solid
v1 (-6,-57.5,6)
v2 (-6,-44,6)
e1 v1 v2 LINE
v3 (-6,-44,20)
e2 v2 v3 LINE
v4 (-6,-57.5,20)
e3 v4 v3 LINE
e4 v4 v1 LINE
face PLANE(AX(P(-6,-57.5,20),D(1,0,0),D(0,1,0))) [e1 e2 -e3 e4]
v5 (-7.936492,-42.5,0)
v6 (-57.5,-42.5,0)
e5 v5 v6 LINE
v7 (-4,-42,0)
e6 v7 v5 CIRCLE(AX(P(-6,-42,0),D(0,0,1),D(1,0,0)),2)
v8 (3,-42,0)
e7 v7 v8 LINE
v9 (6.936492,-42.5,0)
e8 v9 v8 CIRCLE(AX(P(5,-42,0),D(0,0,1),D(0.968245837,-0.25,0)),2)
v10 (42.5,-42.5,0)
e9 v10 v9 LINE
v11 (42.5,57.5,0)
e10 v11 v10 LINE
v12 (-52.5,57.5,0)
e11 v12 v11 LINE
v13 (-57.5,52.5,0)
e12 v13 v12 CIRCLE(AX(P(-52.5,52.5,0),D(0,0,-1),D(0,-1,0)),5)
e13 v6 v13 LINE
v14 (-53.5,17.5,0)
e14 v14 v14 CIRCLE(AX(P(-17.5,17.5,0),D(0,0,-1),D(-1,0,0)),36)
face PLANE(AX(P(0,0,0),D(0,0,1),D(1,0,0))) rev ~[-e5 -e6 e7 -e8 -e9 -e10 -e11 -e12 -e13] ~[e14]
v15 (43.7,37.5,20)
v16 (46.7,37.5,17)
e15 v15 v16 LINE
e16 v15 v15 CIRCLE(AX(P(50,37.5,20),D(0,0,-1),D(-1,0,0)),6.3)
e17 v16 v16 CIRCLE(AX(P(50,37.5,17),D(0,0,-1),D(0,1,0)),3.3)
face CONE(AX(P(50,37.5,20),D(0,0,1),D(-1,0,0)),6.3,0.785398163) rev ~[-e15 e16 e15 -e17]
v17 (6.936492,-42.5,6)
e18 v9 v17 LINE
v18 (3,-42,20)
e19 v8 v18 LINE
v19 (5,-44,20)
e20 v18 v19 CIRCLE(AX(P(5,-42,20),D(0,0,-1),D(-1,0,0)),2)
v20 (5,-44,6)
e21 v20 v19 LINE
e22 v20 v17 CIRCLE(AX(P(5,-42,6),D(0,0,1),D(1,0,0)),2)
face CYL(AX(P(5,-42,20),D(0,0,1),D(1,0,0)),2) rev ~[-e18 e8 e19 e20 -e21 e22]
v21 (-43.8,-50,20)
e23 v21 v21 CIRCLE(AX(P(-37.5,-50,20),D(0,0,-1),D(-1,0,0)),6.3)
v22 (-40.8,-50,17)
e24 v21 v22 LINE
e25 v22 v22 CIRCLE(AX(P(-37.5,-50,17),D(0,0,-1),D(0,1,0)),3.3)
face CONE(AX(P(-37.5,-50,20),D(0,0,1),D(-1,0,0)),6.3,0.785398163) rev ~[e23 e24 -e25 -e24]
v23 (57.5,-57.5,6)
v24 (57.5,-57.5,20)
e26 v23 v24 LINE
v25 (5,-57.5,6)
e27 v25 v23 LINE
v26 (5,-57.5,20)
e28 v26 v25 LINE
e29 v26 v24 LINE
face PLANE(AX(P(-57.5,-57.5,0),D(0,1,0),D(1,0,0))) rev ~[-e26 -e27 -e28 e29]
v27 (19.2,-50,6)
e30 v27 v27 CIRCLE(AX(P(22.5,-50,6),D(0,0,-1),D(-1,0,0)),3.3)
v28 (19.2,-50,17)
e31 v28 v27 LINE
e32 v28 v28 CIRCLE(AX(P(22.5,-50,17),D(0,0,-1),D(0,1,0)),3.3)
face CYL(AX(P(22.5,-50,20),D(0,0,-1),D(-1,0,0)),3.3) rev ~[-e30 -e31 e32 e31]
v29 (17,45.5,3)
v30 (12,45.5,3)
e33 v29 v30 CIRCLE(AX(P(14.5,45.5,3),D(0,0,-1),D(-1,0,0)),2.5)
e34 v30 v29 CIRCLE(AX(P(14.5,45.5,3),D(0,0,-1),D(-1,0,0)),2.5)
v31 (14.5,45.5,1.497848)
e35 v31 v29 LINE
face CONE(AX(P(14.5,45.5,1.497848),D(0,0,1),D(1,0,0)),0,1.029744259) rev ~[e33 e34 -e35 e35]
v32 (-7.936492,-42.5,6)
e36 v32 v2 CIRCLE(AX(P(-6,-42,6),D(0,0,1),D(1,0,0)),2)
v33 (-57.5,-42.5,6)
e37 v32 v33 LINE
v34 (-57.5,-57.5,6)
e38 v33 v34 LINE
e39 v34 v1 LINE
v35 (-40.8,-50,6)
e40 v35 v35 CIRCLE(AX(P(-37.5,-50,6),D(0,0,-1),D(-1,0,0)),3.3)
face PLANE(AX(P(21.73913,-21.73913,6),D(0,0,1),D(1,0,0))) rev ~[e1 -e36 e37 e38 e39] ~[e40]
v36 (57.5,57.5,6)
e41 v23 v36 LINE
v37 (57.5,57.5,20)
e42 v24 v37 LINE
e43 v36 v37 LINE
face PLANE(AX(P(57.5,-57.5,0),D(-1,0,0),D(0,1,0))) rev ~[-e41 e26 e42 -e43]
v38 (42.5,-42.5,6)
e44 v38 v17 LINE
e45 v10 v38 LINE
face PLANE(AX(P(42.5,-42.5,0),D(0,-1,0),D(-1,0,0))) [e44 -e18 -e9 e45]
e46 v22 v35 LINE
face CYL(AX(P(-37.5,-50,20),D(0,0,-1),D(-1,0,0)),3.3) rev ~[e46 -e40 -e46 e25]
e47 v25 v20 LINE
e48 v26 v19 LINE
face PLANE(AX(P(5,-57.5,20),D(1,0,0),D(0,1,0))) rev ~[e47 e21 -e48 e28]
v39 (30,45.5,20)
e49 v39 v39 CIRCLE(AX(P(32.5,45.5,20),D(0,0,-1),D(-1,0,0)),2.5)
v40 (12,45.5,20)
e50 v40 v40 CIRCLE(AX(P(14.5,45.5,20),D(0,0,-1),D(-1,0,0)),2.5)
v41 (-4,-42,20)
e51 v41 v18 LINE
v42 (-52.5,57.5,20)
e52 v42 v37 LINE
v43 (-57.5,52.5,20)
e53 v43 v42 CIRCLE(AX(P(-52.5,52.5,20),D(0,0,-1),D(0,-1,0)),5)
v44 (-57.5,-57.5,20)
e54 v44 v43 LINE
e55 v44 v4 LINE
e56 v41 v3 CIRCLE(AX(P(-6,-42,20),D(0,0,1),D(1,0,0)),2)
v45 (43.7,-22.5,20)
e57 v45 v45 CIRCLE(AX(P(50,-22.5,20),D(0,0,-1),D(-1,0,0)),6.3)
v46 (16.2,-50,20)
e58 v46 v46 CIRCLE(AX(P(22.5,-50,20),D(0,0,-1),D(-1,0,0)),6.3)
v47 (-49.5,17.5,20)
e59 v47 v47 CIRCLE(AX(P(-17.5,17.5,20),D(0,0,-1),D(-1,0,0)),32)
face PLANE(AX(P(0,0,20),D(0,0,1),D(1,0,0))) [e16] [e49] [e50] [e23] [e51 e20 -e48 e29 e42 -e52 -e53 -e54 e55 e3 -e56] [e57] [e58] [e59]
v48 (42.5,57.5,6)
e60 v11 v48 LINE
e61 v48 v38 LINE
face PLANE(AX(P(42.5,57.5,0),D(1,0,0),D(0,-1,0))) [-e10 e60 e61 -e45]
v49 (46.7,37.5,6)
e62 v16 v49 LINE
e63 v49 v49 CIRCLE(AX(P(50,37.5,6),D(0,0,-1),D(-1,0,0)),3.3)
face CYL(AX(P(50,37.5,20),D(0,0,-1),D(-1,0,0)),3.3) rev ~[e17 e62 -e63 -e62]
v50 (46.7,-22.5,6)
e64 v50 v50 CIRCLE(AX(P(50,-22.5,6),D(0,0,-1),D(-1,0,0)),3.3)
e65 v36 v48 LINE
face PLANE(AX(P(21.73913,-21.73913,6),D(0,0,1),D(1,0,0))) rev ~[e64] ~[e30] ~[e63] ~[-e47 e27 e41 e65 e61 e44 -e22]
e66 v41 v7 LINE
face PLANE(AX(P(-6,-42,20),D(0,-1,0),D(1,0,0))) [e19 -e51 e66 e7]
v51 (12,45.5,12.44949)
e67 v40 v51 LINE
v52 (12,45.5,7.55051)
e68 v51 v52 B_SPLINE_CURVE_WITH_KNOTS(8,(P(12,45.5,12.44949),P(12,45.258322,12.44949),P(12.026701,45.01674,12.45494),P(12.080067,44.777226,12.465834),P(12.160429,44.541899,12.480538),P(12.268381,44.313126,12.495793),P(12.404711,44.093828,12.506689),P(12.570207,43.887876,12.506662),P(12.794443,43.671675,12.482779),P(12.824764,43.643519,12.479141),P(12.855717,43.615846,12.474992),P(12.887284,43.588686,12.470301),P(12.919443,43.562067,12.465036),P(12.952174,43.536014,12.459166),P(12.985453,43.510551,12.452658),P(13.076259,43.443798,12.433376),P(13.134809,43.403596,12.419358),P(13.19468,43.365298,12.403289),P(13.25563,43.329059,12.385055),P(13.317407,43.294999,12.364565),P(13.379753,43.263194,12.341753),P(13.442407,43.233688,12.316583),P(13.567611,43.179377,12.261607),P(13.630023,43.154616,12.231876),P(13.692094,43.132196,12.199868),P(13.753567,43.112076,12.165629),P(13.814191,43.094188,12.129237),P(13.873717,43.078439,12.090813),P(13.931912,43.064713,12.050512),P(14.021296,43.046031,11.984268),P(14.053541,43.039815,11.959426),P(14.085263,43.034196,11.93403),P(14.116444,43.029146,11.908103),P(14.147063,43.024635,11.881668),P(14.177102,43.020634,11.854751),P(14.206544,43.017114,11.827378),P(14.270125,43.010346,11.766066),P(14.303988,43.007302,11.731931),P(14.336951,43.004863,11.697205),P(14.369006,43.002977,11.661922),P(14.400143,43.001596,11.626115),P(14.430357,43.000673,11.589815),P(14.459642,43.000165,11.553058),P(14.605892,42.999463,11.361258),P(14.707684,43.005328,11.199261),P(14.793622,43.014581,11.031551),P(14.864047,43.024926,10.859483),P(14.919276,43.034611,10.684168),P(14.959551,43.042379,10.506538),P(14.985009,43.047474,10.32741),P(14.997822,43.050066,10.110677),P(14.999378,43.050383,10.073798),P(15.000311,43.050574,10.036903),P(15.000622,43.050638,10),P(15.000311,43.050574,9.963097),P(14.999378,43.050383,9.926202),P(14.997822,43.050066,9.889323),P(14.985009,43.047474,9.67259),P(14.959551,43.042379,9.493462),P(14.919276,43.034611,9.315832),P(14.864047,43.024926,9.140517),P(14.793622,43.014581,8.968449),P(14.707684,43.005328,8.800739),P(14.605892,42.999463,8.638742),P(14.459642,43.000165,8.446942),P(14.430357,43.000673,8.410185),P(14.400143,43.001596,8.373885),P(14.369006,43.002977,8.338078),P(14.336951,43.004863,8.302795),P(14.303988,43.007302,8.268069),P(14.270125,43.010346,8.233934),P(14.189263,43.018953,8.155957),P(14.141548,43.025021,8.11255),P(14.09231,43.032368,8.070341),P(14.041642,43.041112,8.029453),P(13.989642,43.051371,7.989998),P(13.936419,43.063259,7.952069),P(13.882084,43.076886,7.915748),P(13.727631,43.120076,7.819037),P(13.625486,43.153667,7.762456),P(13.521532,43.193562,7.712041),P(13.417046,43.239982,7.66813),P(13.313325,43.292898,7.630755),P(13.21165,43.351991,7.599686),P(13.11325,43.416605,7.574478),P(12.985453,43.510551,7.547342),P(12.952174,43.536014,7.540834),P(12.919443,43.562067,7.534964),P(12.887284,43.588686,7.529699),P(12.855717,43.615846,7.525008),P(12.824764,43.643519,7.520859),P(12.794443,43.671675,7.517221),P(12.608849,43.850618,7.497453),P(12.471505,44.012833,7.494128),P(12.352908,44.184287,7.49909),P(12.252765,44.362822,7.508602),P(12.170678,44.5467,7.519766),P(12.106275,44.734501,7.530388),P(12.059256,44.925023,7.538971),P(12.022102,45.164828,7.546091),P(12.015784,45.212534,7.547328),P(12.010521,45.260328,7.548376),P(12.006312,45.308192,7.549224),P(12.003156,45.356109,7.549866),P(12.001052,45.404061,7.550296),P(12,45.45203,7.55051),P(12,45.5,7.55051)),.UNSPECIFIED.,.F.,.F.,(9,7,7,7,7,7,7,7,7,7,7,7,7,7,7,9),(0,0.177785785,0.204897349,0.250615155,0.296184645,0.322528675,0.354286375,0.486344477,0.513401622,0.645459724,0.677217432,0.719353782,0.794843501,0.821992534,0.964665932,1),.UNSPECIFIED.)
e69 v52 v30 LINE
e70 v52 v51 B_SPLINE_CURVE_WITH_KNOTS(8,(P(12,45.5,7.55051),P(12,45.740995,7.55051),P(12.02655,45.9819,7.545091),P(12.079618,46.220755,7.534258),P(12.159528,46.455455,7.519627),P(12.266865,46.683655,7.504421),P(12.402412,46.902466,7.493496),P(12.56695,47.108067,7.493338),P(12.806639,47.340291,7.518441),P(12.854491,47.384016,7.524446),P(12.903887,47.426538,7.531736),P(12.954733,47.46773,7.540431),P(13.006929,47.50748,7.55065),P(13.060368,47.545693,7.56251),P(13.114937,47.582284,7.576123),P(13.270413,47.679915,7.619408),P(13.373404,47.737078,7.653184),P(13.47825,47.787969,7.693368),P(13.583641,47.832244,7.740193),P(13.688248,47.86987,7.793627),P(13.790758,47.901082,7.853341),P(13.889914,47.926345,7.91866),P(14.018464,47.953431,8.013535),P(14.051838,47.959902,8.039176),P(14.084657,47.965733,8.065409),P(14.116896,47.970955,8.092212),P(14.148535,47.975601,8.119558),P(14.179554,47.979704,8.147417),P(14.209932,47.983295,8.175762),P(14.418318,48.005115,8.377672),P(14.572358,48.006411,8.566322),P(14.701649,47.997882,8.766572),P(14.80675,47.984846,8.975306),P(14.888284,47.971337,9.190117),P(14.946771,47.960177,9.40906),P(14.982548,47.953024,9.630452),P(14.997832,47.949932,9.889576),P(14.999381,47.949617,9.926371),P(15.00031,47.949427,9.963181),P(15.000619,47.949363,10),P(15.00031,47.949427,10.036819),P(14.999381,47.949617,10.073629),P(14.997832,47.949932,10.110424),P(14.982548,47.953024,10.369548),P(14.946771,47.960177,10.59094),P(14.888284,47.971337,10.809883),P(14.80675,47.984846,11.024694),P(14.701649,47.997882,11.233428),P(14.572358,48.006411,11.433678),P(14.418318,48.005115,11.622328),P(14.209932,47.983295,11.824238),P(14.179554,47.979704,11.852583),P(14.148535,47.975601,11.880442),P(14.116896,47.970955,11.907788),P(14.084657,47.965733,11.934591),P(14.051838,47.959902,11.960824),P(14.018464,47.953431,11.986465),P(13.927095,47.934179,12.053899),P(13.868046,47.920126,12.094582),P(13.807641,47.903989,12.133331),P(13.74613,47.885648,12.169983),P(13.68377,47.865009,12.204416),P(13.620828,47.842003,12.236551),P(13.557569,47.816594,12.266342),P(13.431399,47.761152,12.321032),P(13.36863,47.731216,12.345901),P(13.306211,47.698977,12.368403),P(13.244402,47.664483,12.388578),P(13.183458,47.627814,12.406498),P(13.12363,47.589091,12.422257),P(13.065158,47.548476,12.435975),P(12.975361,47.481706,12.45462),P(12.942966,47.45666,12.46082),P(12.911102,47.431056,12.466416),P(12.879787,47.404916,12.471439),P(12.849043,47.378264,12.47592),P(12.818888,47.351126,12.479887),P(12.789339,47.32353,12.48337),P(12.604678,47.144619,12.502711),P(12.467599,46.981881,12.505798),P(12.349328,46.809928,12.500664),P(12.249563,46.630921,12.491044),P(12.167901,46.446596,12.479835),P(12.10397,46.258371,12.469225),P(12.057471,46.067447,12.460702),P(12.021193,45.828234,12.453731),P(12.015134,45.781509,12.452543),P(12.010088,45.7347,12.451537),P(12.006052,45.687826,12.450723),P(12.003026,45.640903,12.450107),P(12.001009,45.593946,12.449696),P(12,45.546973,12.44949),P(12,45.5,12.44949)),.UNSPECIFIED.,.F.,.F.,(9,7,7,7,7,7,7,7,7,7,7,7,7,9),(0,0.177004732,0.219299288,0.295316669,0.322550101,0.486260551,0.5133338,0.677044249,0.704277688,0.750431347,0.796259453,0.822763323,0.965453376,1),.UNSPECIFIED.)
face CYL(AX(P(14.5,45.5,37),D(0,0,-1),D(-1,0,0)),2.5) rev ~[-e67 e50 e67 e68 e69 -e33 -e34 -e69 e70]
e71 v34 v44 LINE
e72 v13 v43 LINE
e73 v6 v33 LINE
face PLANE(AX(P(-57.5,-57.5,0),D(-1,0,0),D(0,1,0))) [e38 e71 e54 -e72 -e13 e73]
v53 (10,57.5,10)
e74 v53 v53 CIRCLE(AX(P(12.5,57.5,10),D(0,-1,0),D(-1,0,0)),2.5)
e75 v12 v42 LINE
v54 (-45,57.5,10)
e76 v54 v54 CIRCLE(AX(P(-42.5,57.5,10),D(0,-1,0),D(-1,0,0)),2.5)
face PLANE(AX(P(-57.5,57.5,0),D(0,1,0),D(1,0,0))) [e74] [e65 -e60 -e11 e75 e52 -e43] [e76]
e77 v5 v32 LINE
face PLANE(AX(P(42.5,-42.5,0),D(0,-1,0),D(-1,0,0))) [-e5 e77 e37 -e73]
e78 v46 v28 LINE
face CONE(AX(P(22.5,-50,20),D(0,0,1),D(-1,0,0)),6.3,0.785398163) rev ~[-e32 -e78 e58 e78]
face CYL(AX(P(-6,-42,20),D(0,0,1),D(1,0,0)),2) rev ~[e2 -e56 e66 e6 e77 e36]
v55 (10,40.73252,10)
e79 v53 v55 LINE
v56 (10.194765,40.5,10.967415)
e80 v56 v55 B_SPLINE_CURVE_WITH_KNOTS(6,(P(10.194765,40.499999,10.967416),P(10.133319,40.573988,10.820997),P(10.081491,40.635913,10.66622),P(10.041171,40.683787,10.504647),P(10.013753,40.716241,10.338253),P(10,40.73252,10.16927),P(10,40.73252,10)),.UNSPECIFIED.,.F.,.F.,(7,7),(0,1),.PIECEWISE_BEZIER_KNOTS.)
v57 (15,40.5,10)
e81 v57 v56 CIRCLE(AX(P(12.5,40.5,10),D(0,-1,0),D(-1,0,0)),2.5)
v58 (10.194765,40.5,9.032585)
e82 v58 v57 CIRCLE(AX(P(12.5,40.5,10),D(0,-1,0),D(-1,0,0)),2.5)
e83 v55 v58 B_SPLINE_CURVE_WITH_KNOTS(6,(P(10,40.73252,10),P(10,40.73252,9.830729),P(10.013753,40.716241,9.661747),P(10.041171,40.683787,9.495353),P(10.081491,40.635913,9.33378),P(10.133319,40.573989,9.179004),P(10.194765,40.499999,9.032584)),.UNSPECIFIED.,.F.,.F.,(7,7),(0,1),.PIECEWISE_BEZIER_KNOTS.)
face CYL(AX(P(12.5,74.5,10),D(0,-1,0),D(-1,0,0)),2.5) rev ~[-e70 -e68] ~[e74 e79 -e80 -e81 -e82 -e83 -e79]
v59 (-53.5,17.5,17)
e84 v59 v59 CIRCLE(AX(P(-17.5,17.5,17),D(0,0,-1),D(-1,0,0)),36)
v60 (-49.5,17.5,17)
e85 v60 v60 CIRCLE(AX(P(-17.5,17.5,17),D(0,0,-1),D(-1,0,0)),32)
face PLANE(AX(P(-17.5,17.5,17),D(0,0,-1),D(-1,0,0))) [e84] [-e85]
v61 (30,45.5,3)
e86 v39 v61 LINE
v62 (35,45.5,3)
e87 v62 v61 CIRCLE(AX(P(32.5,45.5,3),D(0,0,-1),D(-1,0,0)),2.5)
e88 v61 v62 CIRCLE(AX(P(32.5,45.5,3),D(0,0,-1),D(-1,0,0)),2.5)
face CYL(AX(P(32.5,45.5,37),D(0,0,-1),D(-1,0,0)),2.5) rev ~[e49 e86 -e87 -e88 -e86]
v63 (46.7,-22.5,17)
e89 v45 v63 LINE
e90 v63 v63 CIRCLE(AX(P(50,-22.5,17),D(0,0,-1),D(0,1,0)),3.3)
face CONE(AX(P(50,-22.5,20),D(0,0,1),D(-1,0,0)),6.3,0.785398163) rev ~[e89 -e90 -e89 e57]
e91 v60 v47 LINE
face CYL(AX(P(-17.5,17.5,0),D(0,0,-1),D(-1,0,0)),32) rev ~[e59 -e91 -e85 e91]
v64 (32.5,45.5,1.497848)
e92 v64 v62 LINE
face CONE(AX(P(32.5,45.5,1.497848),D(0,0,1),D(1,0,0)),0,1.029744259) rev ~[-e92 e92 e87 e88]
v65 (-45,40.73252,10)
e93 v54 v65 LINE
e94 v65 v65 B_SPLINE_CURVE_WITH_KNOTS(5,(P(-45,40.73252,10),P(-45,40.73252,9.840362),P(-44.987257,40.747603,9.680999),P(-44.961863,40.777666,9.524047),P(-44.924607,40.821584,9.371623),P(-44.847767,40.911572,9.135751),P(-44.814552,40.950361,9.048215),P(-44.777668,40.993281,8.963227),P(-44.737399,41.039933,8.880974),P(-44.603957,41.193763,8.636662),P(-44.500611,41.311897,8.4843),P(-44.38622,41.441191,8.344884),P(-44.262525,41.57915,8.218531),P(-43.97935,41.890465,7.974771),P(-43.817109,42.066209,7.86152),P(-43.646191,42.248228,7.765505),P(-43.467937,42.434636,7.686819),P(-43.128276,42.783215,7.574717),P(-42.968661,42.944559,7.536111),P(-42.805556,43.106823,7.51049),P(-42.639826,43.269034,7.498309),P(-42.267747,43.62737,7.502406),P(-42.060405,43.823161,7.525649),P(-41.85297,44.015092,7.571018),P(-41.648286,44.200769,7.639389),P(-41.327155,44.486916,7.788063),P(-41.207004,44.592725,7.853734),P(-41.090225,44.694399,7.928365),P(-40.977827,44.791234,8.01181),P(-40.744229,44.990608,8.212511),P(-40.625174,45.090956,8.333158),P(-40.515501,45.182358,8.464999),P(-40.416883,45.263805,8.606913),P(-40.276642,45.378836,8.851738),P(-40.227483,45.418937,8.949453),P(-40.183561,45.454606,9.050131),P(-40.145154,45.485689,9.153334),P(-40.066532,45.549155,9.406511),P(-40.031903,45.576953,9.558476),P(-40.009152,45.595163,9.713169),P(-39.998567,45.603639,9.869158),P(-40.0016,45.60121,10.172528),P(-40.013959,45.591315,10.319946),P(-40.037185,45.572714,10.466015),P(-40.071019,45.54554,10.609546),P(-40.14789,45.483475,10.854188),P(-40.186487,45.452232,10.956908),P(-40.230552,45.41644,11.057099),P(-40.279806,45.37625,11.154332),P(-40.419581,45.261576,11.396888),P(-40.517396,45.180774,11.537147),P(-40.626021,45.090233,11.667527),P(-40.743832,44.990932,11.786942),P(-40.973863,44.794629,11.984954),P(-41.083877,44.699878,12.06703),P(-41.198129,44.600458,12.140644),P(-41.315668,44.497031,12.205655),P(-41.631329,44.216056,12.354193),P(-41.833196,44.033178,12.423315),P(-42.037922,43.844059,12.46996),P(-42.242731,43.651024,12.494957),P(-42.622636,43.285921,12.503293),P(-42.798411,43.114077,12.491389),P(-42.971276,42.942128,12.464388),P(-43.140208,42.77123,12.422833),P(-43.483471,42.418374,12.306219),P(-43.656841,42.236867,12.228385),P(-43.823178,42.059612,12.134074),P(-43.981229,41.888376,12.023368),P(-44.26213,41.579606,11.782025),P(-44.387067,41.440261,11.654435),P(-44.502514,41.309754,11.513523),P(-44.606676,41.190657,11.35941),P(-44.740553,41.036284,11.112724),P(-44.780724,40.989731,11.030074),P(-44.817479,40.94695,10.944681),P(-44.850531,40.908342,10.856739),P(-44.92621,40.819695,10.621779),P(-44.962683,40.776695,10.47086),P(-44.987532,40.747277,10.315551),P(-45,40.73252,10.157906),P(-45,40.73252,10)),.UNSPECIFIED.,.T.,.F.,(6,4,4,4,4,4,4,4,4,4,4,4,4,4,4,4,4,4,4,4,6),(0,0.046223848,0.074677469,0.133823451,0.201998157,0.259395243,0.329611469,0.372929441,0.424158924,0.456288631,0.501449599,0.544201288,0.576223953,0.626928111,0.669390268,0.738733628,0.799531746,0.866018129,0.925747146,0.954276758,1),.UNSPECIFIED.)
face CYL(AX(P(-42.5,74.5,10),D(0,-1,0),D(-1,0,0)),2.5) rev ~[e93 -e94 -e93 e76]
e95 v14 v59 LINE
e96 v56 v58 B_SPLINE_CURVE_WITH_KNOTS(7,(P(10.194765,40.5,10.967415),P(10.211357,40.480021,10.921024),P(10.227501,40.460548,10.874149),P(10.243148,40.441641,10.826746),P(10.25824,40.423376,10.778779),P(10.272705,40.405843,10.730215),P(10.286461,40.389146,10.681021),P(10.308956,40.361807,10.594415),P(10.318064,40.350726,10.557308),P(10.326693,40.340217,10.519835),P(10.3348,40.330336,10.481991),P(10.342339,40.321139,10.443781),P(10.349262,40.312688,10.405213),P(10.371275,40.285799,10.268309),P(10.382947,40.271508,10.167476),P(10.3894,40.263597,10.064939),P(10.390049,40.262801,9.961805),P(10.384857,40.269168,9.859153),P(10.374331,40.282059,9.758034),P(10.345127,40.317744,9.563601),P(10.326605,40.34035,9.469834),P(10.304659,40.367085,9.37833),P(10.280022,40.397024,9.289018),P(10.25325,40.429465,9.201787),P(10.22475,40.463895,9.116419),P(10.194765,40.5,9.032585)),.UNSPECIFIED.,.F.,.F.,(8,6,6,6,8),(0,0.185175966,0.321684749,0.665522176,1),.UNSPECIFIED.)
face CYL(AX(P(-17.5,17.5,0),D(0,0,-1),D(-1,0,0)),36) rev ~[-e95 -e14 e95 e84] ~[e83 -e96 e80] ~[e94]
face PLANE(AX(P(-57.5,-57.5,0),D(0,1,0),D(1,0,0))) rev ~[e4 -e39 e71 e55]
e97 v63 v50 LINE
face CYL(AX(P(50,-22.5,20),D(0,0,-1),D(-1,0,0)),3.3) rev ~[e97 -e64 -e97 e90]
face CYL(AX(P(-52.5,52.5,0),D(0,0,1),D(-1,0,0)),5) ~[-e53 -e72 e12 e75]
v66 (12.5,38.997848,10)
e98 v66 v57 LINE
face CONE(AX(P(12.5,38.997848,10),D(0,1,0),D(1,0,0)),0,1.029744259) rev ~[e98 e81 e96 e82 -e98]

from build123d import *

# Parameters (mm, degrees)
SKETCH_1_W                   = 115
SKETCH_1_H                   = 115
EXTRUDE_1_DEPTH              = 20
CUT_EXTRUDE_1_DEPTH          = 6
SKETCH_3_R                   = 32
CUT_EXTRUDE_2_DEPTH          = 84.740671122
SKETCH_4_R                   = 36
CUT_EXTRUDE_3_DEPTH          = 17
SKETCH_5_W                   = 11
SKETCH_5_H                   = 15.5
CUT_EXTRUDE_4_DEPTH          = 84.740671122
SKETCH_6_R                   = 2
CUT_EXTRUDE_5_DEPTH          = 84.740671122
HOLE_WIZARD_M6_1_D           = 6.6
HOLE_WIZARD_M6_1_CSINK_D     = 12.6
HOLE_WIZARD_M6_1_CSINK_ANGLE = 90
FILLET_1_R                   = 5
HOLE_WIZARD_M6_1_2_D         = 5
HOLE_WIZARD_M6_1_2_DEPTH     = 17
HOLE_WIZARD_M6_1_2_TIP       = 1.502151548
HOLE_WIZARD_M6_2_D           = 5
HOLE_WIZARD_M6_2_DEPTH       = 17
HOLE_WIZARD_M6_2_TIP         = 1.502151548


with BuildPart() as part:
    # 草图1 → 凸台-拉伸1 (new body)
    with BuildSketch(Plane.XY):
        Rectangle(SKETCH_1_W, SKETCH_1_H)
    extrude(amount=EXTRUDE_1_DEPTH)

    # 草图2 → 切除-拉伸1 (cut)
    with BuildSketch(Plane(origin=(0, 0, 0), x_dir=(-1, 0, 0), z_dir=(0, 0, -1))):
        Polygon((-57.5, 57.5), (-42.5, 57.5), (-42.5, -42.5), (57.5, -42.5), (57.5, -57.5), (-57.5, -57.5), align=None)
    extrude(amount=-CUT_EXTRUDE_1_DEPTH, mode=Mode.SUBTRACT)

    # 草图3 → 切除-拉伸2 (cut, through all)
    with BuildSketch(Plane(origin=(0, 0, 0), x_dir=(-1, 0, 0), z_dir=(0, 0, -1))):
        with Locations((17.5, 17.5)):
            Circle(SKETCH_3_R)
    extrude(amount=-CUT_EXTRUDE_2_DEPTH, mode=Mode.SUBTRACT)

    # 草图4 → 切除-拉伸3 (cut)
    with BuildSketch(Plane(origin=(0, 0, 0), x_dir=(-1, 0, 0), z_dir=(0, 0, -1))):
        with Locations((17.5, 17.5)):
            Circle(SKETCH_4_R)
    extrude(amount=-CUT_EXTRUDE_3_DEPTH, mode=Mode.SUBTRACT)

    # 草图5 → 切除-拉伸4 (cut, through all)
    with BuildSketch(Plane.XY.offset(20)):
        with Locations((-0.5, -49.75)):
            Rectangle(SKETCH_5_W, SKETCH_5_H)
    extrude(amount=-CUT_EXTRUDE_4_DEPTH, mode=Mode.SUBTRACT)

    # 草图6 → 切除-拉伸5 (cut, through all)
    with BuildSketch(Plane.XY.offset(20)):
        with Locations((-6, -42)):
            Circle(SKETCH_6_R)
        with Locations((5, -42)):
            Circle(SKETCH_6_R)
    extrude(amount=-CUT_EXTRUDE_5_DEPTH, mode=Mode.SUBTRACT)

    # Hole Wizard M6 _1 (through all)
    with Locations(Plane.XY.offset(20)):
        with Locations((-37.5, -50), (22.5, -50), (50, -22.5), (50, 37.5)):
            CounterSinkHole(HOLE_WIZARD_M6_1_D / 2, HOLE_WIZARD_M6_1_CSINK_D / 2, counter_sink_angle=HOLE_WIZARD_M6_1_CSINK_ANGLE)

    # 圆角1
    fillet_1_edges = [part.edges().sort_by_distance(p)[0] for p in [
        (-57.5, 57.5, 10),
    ]]
    fillet(fillet_1_edges, radius=FILLET_1_R)

    # Hole Wizard M6 _1 2
    with Locations(Plane.XY.offset(20)):
        with Locations((32.5, 45.5), (14.5, 45.5)):
            Hole(HOLE_WIZARD_M6_1_2_D / 2, depth=HOLE_WIZARD_M6_1_2_DEPTH)
            with Locations((0, 0, -(HOLE_WIZARD_M6_1_2_DEPTH + HOLE_WIZARD_M6_1_2_TIP / 2))):  # 118° drill point
                Cone(0, HOLE_WIZARD_M6_1_2_D / 2, HOLE_WIZARD_M6_1_2_TIP, mode=Mode.SUBTRACT)

    # M6 螺纹孔2
    with Locations(Plane(origin=(0, 57.5, 0), x_dir=(1, 0, 0), z_dir=(0, 1, 0))):
        with Locations((-42.5, -10), (12.5, -10)):
            Hole(HOLE_WIZARD_M6_2_D / 2, depth=HOLE_WIZARD_M6_2_DEPTH)
            with Locations((0, 0, -(HOLE_WIZARD_M6_2_DEPTH + HOLE_WIZARD_M6_2_TIP / 2))):  # 118° drill point
                Cone(0, HOLE_WIZARD_M6_2_D / 2, HOLE_WIZARD_M6_2_TIP, mode=Mode.SUBTRACT)


solid = part.part
